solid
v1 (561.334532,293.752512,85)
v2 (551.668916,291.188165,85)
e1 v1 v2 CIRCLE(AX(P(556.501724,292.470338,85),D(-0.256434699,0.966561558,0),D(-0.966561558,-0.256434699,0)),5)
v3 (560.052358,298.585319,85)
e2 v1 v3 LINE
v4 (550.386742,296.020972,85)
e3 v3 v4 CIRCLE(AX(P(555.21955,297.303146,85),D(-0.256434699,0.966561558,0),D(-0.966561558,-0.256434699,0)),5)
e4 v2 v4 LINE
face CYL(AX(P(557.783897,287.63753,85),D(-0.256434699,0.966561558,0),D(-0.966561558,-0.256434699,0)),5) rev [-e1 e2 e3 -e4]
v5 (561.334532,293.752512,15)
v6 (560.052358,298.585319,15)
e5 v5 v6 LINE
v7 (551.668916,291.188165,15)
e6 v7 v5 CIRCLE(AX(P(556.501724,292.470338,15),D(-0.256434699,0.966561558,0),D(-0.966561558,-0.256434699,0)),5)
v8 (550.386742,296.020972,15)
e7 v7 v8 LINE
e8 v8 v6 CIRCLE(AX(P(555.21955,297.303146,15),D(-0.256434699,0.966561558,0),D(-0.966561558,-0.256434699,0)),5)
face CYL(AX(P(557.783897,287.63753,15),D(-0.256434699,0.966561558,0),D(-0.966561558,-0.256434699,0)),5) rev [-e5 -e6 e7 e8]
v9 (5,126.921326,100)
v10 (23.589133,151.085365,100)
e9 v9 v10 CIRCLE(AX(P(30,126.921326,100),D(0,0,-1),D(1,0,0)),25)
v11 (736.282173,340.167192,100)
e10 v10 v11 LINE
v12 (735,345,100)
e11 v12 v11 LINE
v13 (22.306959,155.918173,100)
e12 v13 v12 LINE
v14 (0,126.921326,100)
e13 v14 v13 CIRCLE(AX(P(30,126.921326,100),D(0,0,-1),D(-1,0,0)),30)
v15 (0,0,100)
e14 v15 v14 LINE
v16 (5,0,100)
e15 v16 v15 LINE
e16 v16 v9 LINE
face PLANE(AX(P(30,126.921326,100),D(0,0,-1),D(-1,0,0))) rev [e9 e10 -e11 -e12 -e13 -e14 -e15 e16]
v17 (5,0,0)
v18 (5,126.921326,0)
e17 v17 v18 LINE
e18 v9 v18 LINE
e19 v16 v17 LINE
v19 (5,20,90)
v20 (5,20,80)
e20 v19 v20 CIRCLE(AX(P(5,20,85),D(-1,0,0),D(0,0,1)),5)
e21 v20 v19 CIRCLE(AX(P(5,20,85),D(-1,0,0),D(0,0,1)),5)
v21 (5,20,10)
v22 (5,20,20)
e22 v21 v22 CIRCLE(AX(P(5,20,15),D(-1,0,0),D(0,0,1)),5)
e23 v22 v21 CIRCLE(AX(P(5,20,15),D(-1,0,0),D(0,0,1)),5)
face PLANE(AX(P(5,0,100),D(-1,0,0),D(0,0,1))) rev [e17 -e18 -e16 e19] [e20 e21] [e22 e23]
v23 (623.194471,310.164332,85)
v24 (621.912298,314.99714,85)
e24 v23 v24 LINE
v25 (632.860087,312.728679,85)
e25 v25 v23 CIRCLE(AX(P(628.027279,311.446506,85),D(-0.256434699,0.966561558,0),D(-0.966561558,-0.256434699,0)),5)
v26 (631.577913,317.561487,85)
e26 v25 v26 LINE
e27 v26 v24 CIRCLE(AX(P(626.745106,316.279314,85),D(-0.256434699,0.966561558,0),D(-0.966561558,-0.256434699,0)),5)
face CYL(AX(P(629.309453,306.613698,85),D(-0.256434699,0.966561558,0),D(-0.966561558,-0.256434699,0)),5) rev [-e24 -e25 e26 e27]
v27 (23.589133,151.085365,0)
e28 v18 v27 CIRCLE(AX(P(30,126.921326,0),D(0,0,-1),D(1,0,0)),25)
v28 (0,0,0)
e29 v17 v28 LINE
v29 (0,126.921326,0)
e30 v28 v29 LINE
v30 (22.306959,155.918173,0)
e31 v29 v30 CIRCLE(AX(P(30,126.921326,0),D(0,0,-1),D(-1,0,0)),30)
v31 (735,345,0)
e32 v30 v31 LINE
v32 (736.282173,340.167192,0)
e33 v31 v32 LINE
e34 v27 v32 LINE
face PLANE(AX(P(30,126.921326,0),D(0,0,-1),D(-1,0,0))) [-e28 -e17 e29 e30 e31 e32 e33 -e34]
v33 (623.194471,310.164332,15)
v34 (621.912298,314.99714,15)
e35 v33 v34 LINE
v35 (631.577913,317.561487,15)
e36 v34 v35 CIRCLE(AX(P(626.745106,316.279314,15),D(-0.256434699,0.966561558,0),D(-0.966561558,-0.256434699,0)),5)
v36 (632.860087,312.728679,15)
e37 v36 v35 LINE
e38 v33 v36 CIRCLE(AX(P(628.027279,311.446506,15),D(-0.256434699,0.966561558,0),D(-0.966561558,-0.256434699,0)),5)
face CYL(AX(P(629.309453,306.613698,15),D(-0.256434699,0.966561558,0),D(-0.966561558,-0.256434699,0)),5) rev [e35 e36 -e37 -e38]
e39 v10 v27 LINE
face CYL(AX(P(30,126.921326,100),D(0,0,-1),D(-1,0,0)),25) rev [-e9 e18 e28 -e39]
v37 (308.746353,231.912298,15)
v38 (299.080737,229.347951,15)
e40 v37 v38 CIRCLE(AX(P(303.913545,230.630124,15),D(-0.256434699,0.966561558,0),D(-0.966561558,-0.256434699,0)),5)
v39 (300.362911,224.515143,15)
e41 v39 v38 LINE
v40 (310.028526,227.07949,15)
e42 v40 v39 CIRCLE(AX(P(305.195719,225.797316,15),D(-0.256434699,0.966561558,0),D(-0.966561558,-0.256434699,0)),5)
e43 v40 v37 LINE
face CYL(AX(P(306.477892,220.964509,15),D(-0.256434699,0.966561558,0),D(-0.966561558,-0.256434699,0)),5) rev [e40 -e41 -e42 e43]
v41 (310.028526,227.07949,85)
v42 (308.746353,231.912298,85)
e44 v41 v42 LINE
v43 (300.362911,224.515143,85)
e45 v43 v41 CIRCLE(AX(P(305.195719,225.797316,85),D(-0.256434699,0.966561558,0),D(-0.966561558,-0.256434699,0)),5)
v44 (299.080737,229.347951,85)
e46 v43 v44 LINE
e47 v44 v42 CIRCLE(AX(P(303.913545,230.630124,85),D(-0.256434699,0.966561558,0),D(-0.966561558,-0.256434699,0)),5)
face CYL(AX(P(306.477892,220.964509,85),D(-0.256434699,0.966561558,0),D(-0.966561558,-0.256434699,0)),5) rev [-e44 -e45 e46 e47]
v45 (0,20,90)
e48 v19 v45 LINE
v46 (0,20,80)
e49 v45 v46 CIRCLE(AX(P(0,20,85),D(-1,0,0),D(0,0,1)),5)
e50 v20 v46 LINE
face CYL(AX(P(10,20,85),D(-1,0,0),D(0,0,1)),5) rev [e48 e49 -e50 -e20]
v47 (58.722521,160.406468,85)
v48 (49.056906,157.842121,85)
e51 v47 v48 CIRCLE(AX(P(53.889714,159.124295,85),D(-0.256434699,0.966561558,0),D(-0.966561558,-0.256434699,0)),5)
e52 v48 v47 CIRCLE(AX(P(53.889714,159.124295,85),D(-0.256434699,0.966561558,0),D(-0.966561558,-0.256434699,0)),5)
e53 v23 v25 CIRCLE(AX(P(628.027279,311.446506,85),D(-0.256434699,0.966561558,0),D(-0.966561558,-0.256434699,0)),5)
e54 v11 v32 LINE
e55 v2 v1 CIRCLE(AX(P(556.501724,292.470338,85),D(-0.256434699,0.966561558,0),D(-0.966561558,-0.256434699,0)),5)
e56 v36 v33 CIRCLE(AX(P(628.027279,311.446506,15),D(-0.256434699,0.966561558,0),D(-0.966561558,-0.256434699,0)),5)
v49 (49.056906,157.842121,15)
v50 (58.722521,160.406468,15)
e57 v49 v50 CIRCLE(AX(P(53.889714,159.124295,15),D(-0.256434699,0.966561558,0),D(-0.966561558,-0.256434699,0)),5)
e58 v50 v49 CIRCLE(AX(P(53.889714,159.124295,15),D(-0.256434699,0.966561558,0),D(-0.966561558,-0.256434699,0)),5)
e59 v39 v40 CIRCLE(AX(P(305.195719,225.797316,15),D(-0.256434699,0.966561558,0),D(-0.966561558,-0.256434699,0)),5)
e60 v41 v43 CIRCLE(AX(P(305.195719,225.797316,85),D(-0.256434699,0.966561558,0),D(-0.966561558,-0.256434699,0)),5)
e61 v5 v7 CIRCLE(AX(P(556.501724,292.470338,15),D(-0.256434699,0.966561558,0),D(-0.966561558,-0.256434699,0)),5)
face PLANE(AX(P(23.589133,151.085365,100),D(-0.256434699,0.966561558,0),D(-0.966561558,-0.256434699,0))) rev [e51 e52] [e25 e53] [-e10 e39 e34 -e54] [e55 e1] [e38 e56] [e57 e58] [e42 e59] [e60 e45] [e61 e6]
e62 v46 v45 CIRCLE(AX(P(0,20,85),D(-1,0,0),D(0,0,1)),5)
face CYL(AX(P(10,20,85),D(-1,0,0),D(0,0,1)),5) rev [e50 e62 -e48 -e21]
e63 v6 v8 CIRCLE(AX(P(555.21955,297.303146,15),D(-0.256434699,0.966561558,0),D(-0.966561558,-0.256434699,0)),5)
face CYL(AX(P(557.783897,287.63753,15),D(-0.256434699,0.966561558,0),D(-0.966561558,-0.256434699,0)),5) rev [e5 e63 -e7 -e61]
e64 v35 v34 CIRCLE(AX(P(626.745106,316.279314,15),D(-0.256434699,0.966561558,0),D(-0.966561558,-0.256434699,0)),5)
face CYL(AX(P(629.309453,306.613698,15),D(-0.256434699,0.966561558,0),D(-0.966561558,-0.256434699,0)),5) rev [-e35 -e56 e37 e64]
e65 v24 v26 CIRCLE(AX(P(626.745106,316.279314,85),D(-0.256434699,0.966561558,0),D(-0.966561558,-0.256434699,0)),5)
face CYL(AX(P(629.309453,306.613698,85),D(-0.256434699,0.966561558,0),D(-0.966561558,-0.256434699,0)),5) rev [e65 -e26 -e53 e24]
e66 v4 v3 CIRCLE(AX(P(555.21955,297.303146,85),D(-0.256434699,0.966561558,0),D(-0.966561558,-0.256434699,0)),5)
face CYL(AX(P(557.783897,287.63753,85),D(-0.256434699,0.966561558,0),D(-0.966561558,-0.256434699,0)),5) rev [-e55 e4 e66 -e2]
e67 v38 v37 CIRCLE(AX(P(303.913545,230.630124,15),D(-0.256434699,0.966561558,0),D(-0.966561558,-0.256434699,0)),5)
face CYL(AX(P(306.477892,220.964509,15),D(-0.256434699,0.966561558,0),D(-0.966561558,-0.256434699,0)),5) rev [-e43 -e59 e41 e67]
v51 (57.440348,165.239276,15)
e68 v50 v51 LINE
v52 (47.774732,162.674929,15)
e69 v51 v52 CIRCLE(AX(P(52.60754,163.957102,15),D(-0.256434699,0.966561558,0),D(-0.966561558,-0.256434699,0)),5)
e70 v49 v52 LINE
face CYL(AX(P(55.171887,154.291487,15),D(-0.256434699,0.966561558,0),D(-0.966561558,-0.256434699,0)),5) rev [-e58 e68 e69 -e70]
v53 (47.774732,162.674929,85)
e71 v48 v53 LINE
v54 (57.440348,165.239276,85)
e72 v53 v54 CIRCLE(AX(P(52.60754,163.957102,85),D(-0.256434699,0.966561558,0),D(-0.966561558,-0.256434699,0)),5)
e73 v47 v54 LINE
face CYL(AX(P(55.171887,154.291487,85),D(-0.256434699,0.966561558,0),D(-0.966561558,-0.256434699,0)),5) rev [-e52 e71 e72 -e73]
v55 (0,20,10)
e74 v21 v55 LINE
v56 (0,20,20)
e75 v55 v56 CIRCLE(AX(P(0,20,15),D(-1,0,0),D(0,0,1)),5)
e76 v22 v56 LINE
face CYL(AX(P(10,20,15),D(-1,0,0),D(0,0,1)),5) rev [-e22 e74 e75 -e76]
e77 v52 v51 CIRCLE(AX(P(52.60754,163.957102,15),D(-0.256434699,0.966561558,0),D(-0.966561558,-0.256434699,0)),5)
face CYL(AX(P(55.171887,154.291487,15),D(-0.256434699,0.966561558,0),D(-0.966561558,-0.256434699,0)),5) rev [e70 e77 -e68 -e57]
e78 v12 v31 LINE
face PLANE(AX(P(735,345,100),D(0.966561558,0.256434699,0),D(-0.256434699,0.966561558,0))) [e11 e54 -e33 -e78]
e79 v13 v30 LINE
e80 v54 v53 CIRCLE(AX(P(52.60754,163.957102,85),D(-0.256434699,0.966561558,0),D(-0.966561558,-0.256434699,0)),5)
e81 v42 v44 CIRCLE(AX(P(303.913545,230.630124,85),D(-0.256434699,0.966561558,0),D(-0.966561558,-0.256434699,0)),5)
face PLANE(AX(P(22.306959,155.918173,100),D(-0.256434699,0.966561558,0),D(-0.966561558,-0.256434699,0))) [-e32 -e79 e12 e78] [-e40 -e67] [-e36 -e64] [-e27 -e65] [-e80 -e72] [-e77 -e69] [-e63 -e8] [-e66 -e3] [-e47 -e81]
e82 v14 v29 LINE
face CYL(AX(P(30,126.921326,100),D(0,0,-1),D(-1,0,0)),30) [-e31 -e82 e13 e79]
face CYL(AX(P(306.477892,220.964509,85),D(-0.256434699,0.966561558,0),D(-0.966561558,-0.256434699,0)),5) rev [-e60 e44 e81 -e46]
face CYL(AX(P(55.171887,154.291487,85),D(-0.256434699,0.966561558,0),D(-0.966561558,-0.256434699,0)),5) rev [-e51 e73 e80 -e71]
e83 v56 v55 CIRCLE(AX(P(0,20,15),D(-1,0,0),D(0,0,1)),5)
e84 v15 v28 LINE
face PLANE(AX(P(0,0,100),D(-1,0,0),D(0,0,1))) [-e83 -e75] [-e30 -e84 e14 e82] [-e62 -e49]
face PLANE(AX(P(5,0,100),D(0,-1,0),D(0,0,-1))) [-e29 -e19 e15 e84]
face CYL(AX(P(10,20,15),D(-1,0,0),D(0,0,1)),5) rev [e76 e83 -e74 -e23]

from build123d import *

# Parameters (mm, degrees)
EXTRUDE_THIN1_DEPTH  = 100
SKETCH2_R            = 5
CUT_EXTRUDE1_DEPTH   = 10
LPATTERN1_COUNT      = 2
LPATTERN1_PITCH      = 70
SKETCH3_R            = 5
CUT_EXTRUDE2_DEPTH   = 10
LPATTERN2_COUNT      = 3
LPATTERN2_PITCH      = 260
LPATTERN2_COUNT_DIR2 = 2
LPATTERN2_PITCH_DIR2 = 70
SKETCH4_R            = 5
CUT_EXTRUDE3_DEPTH   = 10
LPATTERN3_COUNT      = 2
LPATTERN3_PITCH      = 70


with BuildPart() as part:
    # Sketch1 → Extrude-Thin1 (new body)
    with BuildSketch(Plane.XY):
        with BuildLine():
            Line((0, 0), (0, 126.921326068))
            ThreePointArc((0, 126.921326068), (6.221950993, 145.213520727), (22.306959029, 155.918172804))
            Line((22.306959029, 155.918172804), (735, 345))
            Line((735, 345), (736.282173495, 340.167192211))
            Line((736.282173495, 340.167192211), (23.589132524, 151.085365014))
            ThreePointArc((23.589132524, 151.085365014), (10.184959161, 142.164821617), (5, 126.921326068))
            Line((5, 126.921326068), (5, 0))
            Line((5, 0), (0, 0))
        make_face()
    extrude(amount=EXTRUDE_THIN1_DEPTH)

    # Sketch2 → Cut-Extrude1 (cut)
    with BuildSketch(Plane(origin=(-37.178988327, 140.13618677, 0), x_dir=(0.9665615578617778, 0.25643469902455335, 0), z_dir=(-0.25643469902455335, 0.9665615578617778, 0))):
        with Locations(Location((686.892716192, -15, 0), (0, 0, 180))):
            Circle(SKETCH2_R)
    cut_extrude1 = extrude(amount=-CUT_EXTRUDE1_DEPTH, mode=Mode.SUBTRACT)

    # LPattern1: Cut-Extrude1 ×2
    with Locations(*[(0, 0, i * LPATTERN1_PITCH) for i in range(1, LPATTERN1_COUNT)]):
        add(cut_extrude1, mode=Mode.SUBTRACT)

    # Sketch3 → Cut-Extrude2 (cut)
    with BuildSketch(Plane(origin=(-37.178988327, 140.13618677, 0), x_dir=(0.9665615578617778, 0.25643469902455335, 0), z_dir=(-0.25643469902455335, 0.9665615578617778, 0))):
        with Locations(Location((612.892716192, -15, 0), (0, 0, 180))):
            Circle(SKETCH3_R)
    cut_extrude2 = extrude(amount=-CUT_EXTRUDE2_DEPTH, mode=Mode.SUBTRACT)

    # LPattern2: Cut-Extrude2 3 × 2
    with Locations(*[Vector(-0.9665615578617778, -0.25643469902455335, 0) * (i * LPATTERN2_PITCH) + Vector(0, 0, 1) * (j * LPATTERN2_PITCH_DIR2) for i in range(LPATTERN2_COUNT) for j in range(LPATTERN2_COUNT_DIR2) if (i, j) != (0, 0)]):
        add(cut_extrude2, mode=Mode.SUBTRACT)

    # Sketch4 → Cut-Extrude3 (cut)
    with BuildSketch(Plane.ZY):
        with Locations((85, 20)):
            Circle(SKETCH4_R)
    cut_extrude3 = extrude(amount=-CUT_EXTRUDE3_DEPTH, mode=Mode.SUBTRACT)

    # LPattern3: Cut-Extrude3 ×2
    with Locations(*[(0, 0, -i * LPATTERN3_PITCH) for i in range(1, LPATTERN3_COUNT)]):
        add(cut_extrude3, mode=Mode.SUBTRACT)


solid = part.part
